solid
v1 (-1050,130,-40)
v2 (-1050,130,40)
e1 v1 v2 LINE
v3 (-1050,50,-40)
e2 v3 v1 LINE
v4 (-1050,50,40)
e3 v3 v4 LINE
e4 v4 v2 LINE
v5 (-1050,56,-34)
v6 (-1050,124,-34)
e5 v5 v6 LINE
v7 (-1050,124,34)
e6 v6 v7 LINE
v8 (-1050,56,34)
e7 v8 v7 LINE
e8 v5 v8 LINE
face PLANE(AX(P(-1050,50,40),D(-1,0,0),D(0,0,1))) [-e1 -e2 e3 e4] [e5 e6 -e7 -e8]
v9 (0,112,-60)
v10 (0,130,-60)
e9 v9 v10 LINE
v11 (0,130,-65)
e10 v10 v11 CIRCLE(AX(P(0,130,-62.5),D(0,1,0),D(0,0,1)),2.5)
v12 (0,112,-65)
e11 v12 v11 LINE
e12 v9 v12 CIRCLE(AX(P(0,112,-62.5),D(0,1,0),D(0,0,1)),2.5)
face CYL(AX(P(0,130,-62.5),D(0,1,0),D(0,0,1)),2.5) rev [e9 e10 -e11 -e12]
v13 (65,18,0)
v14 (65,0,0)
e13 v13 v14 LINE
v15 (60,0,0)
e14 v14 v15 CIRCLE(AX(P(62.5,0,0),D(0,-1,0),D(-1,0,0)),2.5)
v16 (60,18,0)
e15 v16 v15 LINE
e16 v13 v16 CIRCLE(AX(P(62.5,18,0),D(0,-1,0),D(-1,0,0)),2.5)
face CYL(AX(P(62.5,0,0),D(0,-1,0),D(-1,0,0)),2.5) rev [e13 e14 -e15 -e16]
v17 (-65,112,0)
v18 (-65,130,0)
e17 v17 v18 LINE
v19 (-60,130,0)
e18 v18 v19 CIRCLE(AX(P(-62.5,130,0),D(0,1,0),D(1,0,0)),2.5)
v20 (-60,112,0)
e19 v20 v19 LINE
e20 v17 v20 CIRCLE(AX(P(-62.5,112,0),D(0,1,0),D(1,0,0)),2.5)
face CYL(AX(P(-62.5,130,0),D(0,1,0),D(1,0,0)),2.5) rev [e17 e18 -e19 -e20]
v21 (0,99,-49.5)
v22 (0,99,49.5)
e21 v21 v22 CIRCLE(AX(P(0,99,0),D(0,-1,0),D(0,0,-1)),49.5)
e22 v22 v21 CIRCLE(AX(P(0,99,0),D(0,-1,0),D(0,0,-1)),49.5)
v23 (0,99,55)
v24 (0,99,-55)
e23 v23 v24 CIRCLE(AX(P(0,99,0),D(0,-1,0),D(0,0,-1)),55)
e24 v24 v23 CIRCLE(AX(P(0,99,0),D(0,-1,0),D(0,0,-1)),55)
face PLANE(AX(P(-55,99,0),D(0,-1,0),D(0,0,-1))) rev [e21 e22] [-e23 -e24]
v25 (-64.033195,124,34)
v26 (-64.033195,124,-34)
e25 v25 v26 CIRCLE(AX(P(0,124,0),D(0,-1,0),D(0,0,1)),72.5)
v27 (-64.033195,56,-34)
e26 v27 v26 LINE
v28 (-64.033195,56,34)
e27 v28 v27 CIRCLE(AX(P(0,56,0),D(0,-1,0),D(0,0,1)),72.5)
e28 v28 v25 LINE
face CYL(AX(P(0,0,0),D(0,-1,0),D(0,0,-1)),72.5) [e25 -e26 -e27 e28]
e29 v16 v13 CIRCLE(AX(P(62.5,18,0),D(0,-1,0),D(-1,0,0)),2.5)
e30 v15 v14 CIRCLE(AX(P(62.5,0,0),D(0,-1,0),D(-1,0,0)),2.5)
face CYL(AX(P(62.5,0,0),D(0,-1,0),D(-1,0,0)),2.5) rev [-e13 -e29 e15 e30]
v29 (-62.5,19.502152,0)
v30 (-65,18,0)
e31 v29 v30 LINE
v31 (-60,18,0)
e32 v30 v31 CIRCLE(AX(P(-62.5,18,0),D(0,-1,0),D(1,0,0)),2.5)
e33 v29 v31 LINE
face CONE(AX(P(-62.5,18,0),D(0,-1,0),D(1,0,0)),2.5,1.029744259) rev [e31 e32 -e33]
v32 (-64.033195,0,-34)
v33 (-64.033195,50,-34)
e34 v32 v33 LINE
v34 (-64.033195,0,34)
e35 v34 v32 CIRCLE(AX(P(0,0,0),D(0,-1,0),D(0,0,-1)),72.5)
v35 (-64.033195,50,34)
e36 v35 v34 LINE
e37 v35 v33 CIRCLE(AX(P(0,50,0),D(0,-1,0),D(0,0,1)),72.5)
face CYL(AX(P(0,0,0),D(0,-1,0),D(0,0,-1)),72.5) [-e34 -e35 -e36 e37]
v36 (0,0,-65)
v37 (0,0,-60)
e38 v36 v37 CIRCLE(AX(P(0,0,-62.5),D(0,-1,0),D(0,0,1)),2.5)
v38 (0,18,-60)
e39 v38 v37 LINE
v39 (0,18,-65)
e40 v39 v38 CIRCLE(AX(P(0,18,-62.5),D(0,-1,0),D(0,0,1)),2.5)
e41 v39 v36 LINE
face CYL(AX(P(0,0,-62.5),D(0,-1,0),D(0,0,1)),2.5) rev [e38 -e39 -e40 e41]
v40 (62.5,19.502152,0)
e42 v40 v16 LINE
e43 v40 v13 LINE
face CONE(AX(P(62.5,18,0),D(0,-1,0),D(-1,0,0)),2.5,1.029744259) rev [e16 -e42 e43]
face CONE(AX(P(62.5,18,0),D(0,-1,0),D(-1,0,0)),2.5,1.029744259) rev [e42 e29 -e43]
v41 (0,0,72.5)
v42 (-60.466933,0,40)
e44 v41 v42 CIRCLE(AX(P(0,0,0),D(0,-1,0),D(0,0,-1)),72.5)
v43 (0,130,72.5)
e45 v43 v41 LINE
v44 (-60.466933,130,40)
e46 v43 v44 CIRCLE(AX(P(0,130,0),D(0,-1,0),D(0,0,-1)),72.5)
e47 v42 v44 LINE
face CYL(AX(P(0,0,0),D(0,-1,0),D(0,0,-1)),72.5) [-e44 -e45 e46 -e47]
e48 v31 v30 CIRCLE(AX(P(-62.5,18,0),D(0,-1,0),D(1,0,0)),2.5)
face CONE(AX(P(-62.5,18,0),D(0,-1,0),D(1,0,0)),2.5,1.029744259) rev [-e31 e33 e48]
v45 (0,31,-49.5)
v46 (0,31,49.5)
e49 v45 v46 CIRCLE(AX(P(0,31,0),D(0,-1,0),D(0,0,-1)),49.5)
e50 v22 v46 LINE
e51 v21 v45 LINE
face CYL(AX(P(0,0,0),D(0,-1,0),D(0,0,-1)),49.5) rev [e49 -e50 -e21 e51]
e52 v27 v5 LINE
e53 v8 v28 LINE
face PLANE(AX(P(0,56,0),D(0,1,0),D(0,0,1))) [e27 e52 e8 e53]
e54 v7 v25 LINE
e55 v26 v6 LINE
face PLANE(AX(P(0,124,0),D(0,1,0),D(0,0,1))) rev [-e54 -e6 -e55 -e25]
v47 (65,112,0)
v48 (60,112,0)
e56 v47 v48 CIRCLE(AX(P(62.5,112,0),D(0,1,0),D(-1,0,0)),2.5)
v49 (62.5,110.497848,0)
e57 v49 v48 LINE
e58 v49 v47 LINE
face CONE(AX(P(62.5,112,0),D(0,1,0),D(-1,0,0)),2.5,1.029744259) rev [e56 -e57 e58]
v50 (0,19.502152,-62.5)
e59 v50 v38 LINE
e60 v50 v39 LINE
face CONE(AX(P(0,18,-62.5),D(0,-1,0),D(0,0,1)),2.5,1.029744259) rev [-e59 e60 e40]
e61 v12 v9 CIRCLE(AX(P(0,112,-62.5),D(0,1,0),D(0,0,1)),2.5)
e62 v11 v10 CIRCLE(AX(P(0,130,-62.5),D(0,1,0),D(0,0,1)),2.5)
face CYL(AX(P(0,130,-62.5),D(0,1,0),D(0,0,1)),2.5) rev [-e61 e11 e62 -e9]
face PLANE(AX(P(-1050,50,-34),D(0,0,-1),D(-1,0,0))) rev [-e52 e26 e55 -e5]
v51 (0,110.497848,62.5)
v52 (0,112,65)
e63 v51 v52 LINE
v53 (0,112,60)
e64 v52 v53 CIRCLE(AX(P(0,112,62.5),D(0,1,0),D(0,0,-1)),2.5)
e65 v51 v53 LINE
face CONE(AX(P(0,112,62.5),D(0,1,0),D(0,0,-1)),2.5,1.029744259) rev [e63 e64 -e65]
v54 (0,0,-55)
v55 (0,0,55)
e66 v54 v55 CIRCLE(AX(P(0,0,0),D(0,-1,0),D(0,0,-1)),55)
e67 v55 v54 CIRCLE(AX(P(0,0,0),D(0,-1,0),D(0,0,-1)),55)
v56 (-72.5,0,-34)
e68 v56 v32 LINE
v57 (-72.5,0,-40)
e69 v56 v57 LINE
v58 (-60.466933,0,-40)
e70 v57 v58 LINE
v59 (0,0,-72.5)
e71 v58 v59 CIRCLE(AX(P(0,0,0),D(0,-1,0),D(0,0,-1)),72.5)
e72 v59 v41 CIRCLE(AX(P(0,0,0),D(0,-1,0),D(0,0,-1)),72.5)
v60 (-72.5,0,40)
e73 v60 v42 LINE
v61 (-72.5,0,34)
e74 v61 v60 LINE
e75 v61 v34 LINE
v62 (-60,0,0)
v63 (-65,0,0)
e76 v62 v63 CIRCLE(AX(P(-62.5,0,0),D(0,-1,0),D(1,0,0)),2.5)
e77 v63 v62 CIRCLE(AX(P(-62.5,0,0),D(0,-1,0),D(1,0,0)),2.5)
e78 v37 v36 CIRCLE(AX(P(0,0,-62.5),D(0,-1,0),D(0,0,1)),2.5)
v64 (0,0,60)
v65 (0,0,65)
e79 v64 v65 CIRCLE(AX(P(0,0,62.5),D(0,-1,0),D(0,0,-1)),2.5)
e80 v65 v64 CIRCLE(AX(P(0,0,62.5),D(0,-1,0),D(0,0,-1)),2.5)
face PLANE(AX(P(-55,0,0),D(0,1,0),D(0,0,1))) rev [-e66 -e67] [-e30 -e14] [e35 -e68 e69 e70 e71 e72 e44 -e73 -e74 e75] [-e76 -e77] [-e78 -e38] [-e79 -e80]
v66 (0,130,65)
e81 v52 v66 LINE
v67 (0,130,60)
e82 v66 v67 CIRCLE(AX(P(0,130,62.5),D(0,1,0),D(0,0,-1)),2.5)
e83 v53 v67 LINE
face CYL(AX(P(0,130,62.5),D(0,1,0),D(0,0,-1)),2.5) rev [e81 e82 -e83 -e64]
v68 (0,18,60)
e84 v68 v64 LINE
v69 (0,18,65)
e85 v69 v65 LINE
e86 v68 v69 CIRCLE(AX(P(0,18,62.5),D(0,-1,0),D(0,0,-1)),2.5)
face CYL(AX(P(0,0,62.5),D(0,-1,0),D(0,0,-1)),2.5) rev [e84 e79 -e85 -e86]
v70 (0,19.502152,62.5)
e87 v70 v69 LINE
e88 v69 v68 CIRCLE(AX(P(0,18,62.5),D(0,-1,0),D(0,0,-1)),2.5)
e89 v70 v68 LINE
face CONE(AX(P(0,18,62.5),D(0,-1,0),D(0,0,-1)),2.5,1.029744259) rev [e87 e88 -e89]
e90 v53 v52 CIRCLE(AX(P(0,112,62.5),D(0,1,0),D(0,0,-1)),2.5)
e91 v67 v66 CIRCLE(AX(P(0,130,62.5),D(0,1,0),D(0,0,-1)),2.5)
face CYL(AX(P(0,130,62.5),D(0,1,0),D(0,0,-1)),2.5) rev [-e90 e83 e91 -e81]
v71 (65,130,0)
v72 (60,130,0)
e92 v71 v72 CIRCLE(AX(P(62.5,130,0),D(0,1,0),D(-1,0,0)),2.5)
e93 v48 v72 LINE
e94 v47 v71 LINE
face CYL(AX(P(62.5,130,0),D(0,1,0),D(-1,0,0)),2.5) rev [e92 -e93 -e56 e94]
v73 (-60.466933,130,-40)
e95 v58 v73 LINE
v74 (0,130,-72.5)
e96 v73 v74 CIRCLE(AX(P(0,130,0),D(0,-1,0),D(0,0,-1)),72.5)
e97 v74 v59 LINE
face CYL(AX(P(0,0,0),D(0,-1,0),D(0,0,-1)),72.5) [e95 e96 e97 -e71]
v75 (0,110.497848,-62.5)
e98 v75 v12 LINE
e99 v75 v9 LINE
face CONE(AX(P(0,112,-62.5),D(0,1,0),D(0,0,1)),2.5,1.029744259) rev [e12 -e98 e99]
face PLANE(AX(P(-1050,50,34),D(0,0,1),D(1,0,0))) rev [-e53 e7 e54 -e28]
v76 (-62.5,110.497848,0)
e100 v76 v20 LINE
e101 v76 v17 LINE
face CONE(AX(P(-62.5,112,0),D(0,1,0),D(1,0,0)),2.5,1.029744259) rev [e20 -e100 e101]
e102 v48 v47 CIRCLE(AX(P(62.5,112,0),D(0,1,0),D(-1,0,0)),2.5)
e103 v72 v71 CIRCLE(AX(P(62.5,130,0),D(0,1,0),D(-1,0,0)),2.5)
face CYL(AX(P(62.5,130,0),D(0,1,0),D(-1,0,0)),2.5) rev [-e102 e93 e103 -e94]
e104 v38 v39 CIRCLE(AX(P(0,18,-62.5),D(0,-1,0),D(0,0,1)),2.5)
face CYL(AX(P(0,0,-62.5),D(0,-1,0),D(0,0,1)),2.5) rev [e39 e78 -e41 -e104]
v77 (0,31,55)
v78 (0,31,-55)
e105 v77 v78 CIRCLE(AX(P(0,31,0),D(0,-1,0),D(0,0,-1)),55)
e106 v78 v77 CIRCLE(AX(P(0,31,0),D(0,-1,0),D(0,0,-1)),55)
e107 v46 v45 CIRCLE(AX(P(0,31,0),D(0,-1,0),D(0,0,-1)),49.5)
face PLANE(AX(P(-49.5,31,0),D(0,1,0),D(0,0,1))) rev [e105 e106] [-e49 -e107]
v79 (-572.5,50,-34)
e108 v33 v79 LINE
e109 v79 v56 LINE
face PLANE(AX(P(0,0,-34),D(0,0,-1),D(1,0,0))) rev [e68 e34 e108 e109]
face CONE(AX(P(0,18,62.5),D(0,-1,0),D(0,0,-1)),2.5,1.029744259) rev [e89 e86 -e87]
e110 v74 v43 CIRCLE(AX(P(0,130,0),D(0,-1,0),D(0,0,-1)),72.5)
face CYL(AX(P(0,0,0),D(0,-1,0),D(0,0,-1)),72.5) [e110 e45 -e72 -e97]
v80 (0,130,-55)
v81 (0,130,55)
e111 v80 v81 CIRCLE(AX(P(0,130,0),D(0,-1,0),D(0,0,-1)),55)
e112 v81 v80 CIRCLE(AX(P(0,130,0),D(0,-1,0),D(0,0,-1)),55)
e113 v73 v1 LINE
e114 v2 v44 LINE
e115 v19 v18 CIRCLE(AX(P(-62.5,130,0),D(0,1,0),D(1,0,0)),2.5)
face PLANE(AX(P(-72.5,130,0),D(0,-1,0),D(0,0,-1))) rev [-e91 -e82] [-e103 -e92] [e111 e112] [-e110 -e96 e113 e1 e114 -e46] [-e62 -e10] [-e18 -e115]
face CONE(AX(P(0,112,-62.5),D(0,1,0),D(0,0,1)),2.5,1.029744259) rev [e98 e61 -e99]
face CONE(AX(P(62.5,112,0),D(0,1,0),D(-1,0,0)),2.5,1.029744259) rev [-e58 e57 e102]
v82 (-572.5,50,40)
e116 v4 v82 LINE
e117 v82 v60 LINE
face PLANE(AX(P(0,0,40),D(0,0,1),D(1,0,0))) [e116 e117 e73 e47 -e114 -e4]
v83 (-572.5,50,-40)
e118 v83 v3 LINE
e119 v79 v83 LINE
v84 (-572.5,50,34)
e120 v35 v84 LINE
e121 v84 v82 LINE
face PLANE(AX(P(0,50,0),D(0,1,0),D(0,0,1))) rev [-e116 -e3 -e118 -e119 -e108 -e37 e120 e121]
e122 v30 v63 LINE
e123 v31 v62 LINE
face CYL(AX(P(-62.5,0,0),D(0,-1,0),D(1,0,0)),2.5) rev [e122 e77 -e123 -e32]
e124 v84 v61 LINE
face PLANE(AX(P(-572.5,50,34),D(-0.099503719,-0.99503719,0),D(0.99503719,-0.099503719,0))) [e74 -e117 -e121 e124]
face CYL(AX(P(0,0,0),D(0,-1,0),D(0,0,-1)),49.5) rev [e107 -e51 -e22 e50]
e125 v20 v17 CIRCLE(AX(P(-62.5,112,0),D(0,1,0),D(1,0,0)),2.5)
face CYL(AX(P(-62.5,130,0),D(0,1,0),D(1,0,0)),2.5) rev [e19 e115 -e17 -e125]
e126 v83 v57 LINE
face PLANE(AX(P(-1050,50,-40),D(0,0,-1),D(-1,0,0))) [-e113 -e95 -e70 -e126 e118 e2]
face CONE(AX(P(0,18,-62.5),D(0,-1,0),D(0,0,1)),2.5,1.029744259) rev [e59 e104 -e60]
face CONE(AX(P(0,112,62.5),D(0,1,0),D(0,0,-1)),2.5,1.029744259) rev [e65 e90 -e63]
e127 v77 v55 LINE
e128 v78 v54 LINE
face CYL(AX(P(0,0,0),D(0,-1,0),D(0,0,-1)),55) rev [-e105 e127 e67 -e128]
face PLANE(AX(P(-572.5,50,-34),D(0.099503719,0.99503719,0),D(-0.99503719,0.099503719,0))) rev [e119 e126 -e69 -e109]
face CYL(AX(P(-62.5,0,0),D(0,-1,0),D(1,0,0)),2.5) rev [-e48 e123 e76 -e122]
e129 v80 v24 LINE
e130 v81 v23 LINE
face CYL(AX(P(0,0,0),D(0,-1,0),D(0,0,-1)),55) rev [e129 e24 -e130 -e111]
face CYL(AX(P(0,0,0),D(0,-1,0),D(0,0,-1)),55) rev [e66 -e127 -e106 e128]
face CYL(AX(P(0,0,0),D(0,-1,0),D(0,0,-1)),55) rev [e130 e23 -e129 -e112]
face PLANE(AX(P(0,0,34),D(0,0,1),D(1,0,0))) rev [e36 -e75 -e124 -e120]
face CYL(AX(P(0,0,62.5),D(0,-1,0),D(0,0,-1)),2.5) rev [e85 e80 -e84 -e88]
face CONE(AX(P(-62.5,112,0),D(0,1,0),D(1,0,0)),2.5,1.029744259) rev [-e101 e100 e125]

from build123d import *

# Parameters (mm, degrees)
CIRPATTERN1_COUNT   = 4
CIRPATTERN2_COUNT   = 4
BOSS_EXTRUDE1_DEPTH = 80
SHELL1_T            = -6
BOSS_EXTRUDE3_DEPTH = 6


with BuildPart() as part:
    # Sketch1 → Revolve1 (revolve)
    with BuildSketch(Plane.XY, mode=Mode.PRIVATE) as revolve1_sk:
        Polygon((-55, 0), (-72.5, 0), (-72.5, 130), (-55, 130), (-55, 99), (-49.5, 99), (-49.5, 31), (-55, 31), align=None)
    revolve(revolve1_sk.sketch.rotate(Axis((0, 0, 0), (0, 1, 0)), 270), axis=Axis((0, 0, 0), (0, 1, 0)))

    # Sketch2 → M6 Tapped Hole1 (revolve, cut)
    with BuildSketch(Plane(origin=(0, 130, -62.5), x_dir=(0, 0, 1), z_dir=(1, 0, 0))):
        Polygon((0, 0), (0, 19.502151548), (2.5, 18), (2.5, 0), align=None)
    m6_tapped_hole1 = revolve(axis=Axis((0, 136.35, -62.5), (0, -1, 0)), mode=Mode.SUBTRACT)

    # CirPattern1: M6 Tapped Hole1 ×4 about axis
    cirpattern1_axis = Axis((0, 0, 0), (0, 1, 0))
    for i in range(1, CIRPATTERN1_COUNT):
        add(m6_tapped_hole1.rotate(cirpattern1_axis, i * 360 / CIRPATTERN1_COUNT), mode=Mode.SUBTRACT)

    # Sketch4 → M6 Tapped Hole2 (revolve, cut)
    with BuildSketch(Plane(origin=(0, 0, 62.5), x_dir=(0, 0, -1), z_dir=(1, 0, 0))):
        Polygon((0, 0), (0, 19.502151548), (2.5, 18), (2.5, 0), align=None)
    m6_tapped_hole2 = revolve(axis=Axis((0, -6.35, 62.5), (0, 1, 0)), mode=Mode.SUBTRACT)

    # CirPattern2: M6 Tapped Hole2 ×4 about axis
    cirpattern2_axis = Axis((0, 0, 0), (0, 1, 0))
    for i in range(1, CIRPATTERN2_COUNT):
        add(m6_tapped_hole2.rotate(cirpattern2_axis, i * 360 / CIRPATTERN2_COUNT), mode=Mode.SUBTRACT)



with BuildPart() as body_2:
    # Sketch6 → Boss-Extrude1 (new body)
    with BuildSketch(Plane(origin=(0, 130, 0), x_dir=(1, 0, 0), z_dir=(0, 1, 0))):
        with BuildLine():
            Line((-1050, 40), (-60.466933112, 40))
            ThreePointArc((-60.466933112, 40), (-72.5, 0), (-60.466933112, -40))
            Line((-60.466933112, -40), (-1050, -40))
            Line((-1050, -40), (-1050, 40))
        make_face()
    extrude(amount=-BOSS_EXTRUDE1_DEPTH)

    # Shell1
    shell1_openings = [body_2.faces().sort_by_distance(p)[0] for p in [
        (-72.5, 90, 0),
        (-1050, 90, 0),
    ]]
    offset(amount=SHELL1_T, openings=shell1_openings, kind=Kind.INTERSECTION)


with BuildPart() as part_1:
    add(part.part)

    add(body_2.part)  # Boss-Extrude3 merges body 2
    # Sketch8 → Boss-Extrude3 (add)
    with BuildSketch(Plane.XY.offset(40)):
        Polygon((-60.466933112, 50), (-572.5, 50), (-72.5, 0), (-60.466933112, 0), align=None)
    boss_extrude3 = extrude(amount=-BOSS_EXTRUDE3_DEPTH)

    # Mirror1: Boss-Extrude3 across plane
    add(boss_extrude3.mirror(Plane.XY))


solid = part_1.part
